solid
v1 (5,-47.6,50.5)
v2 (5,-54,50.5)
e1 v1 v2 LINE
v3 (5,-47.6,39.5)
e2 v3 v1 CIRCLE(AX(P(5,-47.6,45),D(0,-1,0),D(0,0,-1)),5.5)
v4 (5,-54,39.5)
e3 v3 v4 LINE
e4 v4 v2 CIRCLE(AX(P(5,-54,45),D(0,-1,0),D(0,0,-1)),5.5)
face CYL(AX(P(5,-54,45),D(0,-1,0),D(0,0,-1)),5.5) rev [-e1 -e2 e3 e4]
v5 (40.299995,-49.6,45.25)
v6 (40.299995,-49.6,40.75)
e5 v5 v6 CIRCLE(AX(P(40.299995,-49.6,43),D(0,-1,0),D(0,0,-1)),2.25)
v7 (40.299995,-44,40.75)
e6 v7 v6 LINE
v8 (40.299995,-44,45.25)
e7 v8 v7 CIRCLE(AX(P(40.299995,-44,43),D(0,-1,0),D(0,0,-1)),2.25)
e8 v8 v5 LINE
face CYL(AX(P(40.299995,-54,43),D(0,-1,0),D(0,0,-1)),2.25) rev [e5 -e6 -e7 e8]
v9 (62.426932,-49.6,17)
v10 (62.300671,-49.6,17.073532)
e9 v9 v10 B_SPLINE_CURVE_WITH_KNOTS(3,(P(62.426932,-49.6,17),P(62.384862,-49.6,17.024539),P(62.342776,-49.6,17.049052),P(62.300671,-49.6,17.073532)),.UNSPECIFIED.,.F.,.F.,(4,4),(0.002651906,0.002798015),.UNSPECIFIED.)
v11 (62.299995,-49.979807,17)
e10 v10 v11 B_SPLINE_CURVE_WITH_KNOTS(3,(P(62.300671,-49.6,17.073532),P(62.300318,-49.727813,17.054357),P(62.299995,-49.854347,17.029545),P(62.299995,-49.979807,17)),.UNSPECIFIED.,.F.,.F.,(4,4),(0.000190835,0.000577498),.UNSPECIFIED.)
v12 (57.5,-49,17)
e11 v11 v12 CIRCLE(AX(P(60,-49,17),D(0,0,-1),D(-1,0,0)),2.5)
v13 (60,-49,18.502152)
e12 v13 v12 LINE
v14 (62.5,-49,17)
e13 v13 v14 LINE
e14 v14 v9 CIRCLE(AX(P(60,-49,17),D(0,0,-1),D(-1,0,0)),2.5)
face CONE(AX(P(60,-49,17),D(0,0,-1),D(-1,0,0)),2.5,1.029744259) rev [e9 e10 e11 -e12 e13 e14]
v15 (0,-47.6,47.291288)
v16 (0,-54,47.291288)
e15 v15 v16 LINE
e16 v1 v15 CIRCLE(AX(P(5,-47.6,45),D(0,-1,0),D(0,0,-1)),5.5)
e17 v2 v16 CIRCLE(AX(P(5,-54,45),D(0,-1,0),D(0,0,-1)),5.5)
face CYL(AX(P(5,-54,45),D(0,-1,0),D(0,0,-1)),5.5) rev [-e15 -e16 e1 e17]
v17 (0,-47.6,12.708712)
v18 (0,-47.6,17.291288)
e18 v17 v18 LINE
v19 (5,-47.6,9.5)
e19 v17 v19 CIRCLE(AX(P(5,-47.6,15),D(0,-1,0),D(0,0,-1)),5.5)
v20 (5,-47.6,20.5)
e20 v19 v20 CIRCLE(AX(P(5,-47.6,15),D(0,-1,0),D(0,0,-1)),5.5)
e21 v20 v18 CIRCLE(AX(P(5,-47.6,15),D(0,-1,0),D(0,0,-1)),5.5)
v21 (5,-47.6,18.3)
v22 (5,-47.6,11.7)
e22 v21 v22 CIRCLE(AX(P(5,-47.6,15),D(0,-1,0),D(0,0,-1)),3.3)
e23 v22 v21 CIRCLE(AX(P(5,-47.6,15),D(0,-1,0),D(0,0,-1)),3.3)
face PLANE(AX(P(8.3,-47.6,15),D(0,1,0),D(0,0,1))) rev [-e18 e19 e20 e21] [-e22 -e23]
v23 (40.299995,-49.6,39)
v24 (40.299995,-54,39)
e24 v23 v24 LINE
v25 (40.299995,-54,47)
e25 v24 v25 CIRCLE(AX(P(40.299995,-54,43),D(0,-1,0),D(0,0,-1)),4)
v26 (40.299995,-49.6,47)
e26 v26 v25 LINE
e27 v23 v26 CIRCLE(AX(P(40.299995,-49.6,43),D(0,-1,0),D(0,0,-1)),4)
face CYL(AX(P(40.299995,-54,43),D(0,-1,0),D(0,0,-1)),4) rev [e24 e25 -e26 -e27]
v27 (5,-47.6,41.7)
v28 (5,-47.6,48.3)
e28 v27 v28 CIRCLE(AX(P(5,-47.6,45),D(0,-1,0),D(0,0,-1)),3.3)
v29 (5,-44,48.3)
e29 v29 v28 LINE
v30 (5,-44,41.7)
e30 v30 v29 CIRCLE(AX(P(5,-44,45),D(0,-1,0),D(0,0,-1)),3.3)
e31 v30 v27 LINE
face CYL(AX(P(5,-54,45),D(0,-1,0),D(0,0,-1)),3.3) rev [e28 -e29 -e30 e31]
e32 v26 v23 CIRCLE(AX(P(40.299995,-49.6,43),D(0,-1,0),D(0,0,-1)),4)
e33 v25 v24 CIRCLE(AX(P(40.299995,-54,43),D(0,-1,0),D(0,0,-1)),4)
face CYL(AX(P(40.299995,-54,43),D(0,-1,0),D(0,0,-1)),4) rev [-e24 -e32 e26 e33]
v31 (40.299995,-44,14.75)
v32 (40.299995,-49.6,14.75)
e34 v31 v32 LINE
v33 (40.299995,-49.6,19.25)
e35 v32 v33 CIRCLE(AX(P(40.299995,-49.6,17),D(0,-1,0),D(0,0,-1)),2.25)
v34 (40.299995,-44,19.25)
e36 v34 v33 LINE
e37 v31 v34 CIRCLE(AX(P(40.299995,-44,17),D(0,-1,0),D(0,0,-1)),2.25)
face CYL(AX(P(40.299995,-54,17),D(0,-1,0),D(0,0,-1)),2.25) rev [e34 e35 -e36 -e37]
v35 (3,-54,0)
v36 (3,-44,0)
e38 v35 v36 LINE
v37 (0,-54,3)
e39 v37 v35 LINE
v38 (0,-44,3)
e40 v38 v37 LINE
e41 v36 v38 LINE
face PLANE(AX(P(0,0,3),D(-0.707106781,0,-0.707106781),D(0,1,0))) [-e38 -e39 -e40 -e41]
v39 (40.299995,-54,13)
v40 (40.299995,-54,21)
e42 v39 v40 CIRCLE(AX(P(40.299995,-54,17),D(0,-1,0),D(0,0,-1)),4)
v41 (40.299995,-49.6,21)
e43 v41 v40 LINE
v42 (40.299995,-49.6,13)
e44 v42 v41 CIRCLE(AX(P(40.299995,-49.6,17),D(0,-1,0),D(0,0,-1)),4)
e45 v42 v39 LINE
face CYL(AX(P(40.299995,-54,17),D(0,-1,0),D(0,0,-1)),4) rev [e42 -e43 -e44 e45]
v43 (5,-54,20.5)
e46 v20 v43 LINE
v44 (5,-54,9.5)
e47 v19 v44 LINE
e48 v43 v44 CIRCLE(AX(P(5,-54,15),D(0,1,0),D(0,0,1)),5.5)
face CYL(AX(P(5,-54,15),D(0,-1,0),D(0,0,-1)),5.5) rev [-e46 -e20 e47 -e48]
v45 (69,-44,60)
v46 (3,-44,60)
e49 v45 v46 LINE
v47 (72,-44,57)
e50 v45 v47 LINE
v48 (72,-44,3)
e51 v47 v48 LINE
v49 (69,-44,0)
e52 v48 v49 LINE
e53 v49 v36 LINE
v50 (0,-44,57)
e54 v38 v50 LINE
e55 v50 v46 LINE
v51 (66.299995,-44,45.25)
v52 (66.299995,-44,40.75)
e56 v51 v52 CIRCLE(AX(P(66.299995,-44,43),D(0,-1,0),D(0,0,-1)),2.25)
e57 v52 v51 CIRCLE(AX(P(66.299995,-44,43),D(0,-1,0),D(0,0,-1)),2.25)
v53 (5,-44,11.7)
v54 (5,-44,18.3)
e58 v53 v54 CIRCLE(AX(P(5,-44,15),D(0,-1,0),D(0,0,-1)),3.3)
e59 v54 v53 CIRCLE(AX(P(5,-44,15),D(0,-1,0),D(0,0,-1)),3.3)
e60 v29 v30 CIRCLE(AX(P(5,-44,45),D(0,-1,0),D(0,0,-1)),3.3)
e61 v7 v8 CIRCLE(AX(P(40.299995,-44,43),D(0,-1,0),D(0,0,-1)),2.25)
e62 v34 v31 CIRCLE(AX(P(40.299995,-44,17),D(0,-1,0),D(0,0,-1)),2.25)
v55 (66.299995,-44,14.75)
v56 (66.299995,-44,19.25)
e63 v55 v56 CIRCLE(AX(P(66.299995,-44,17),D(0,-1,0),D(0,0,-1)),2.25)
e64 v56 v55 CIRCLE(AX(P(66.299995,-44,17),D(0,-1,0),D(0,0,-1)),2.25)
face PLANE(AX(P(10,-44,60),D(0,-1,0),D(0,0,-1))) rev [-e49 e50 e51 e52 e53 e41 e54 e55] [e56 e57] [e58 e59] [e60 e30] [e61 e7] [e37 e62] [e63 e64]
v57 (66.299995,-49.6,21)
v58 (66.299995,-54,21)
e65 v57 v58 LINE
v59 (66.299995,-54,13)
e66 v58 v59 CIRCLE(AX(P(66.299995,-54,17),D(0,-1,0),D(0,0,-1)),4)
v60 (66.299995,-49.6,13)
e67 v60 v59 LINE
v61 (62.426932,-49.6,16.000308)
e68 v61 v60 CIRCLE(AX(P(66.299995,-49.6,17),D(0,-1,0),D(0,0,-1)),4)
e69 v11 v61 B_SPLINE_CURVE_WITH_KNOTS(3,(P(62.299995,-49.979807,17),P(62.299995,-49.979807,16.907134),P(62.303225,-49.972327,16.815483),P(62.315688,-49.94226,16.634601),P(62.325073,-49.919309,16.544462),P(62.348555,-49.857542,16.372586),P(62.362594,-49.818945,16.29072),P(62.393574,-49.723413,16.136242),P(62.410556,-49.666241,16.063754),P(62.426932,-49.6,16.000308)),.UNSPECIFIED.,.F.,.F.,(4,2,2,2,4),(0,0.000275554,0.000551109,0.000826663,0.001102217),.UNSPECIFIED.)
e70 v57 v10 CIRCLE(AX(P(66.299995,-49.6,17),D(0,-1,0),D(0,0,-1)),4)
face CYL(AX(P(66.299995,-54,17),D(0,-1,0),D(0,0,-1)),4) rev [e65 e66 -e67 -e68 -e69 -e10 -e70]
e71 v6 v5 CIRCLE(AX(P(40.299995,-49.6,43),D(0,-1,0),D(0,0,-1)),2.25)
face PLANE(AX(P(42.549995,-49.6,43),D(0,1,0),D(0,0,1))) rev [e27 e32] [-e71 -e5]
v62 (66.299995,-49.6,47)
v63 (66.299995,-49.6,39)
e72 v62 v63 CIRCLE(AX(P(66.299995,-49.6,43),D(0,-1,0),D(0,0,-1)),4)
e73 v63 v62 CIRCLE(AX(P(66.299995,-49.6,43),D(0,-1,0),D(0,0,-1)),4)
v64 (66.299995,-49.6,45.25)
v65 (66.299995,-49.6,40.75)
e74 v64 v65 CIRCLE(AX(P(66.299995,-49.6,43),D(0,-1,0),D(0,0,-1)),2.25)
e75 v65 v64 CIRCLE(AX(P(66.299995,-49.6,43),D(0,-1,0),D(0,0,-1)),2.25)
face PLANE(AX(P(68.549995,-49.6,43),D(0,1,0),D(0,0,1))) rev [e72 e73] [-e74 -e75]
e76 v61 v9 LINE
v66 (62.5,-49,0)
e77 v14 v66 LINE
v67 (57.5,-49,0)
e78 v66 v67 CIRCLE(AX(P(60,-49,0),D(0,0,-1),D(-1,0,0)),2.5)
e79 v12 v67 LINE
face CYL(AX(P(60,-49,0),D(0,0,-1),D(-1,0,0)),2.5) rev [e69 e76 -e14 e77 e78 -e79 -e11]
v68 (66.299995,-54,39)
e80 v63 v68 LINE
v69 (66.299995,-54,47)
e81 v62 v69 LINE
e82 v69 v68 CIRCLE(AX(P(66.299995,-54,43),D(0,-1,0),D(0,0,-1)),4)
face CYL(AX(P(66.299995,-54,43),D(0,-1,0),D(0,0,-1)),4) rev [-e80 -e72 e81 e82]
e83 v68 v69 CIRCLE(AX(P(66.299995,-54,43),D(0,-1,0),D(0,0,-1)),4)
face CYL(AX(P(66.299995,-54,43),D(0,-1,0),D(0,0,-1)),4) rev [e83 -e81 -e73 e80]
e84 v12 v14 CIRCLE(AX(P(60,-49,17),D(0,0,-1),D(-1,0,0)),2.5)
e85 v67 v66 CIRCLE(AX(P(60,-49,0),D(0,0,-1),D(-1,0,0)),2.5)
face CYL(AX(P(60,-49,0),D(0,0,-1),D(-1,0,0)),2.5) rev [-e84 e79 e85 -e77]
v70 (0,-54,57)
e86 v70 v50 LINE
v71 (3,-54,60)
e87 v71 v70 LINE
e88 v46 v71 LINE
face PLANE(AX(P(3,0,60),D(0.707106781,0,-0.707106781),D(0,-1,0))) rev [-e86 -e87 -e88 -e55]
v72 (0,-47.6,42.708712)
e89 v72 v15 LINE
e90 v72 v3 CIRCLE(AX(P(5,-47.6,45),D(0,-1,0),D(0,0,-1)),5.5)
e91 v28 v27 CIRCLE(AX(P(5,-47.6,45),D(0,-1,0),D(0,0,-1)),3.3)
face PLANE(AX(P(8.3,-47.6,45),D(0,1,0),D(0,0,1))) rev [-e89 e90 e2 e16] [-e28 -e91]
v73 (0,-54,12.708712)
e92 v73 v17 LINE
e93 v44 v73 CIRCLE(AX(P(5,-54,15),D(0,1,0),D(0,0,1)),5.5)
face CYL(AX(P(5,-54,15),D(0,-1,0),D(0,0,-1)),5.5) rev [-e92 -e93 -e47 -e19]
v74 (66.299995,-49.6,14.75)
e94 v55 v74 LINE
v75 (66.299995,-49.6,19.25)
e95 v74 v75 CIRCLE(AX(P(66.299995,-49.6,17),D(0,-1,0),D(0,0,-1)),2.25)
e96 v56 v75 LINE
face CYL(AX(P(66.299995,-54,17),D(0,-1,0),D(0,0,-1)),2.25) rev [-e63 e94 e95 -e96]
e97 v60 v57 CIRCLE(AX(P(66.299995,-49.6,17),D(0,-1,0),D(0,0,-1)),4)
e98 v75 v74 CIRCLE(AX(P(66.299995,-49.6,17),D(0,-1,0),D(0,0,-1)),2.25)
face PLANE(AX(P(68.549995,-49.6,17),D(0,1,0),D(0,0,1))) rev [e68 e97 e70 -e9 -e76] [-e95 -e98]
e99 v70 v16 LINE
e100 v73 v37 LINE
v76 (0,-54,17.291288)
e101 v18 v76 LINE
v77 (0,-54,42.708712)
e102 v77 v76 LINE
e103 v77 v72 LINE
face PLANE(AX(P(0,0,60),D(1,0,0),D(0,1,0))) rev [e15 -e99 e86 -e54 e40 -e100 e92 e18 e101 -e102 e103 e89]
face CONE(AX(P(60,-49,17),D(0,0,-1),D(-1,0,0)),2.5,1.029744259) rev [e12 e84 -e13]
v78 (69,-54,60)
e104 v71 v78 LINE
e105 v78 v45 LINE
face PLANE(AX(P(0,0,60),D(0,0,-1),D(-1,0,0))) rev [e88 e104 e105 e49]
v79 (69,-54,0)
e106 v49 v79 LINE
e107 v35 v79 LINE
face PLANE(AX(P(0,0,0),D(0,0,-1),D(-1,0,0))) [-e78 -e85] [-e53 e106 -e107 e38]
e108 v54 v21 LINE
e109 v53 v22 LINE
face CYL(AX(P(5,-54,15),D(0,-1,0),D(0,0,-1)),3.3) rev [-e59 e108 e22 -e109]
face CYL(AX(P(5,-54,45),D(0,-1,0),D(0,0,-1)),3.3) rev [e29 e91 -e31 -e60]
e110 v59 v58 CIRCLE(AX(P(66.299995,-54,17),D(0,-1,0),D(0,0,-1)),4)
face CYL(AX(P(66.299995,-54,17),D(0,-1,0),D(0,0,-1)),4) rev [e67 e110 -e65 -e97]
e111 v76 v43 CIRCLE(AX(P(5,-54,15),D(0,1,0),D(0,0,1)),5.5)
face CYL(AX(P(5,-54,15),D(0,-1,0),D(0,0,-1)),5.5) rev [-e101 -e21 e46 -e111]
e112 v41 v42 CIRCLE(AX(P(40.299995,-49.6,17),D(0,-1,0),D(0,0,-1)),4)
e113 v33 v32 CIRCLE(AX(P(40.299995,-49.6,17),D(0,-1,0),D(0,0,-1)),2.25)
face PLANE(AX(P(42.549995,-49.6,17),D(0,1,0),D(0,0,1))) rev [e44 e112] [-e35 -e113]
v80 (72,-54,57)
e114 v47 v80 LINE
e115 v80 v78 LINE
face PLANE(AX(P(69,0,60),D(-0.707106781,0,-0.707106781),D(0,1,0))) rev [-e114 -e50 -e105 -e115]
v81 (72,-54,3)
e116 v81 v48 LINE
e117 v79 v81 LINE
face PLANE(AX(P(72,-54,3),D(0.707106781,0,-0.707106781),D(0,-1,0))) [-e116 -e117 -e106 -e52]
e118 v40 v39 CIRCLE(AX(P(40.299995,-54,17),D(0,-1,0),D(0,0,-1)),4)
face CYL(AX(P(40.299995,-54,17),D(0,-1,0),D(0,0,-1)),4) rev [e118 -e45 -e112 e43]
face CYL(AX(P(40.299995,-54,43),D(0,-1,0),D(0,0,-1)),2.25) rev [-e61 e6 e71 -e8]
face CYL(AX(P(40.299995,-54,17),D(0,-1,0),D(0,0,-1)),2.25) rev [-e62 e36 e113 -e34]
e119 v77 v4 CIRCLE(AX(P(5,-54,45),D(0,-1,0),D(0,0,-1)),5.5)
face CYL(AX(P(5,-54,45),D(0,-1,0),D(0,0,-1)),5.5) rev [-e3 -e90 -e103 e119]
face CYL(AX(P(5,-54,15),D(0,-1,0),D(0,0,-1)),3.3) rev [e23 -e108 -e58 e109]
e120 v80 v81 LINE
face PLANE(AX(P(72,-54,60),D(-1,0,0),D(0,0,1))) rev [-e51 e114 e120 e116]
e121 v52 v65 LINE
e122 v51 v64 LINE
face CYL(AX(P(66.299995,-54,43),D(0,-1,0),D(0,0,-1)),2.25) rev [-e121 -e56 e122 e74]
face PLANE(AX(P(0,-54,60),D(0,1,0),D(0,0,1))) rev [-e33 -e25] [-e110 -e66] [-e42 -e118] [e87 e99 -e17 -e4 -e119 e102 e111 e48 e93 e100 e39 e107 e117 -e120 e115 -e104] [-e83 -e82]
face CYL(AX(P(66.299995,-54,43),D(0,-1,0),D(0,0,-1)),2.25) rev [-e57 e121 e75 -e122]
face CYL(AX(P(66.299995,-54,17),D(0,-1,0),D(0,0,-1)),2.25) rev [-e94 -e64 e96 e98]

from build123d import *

# Parameters (mm, degrees)
EXTRUDE_1_DEPTH                = 60
HOLE_WIZARD_M6_2_D             = 5
HOLE_WIZARD_M6_2_DEPTH         = 17
HOLE_WIZARD_M6_2_TIP           = 1.502151548
HOLE_WIZARD_M4_1_D             = 4.5
HOLE_WIZARD_M4_1_DEPTH         = 11.5
HOLE_WIZARD_M4_1_CBORE_D       = 8
HOLE_WIZARD_M4_1_CBORE_DEPTH   = 4.4
HOLE_WIZARD_M4_1_TIP           = 1.351936393
HOLE_WIZARD_M6_1_D             = 5
HOLE_WIZARD_M6_1_DEPTH         = 17
HOLE_WIZARD_M6_1_TIP           = 1.502151548
CHAMFER_1_SIZE                 = 3
SKETCH_9_W                     = 10
SKETCH_9_H                     = 44
CUT_EXTRUDE_1_DEPTH            = 109.166538369
CHAMFER_2_SIZE                 = 3
HOLE_WIZARD_M6_1_2_D           = 6.6
HOLE_WIZARD_M6_1_2_DEPTH       = 17
HOLE_WIZARD_M6_1_2_CBORE_D     = 11
HOLE_WIZARD_M6_1_2_CBORE_DEPTH = 6.4
HOLE_WIZARD_M6_1_2_TIP         = 1.982840043


with BuildPart() as part:
    # 草图2 → 凸台-拉伸1 (new body)
    with BuildSketch(Plane.XY):
        Polygon((0, 0), (0, -54), (72, -54), (72, -44), (10, -44), (10, 0), align=None)
    extrude(amount=EXTRUDE_1_DEPTH)

    # M6 螺纹孔2
    with Locations(Plane(origin=(0, 0, 0), x_dir=(-1, 0, 0), z_dir=(0, 0, -1))):
        with Locations((-60, -49)):
            Hole(HOLE_WIZARD_M6_2_D / 2, depth=HOLE_WIZARD_M6_2_DEPTH)
            with Locations((0, 0, -(HOLE_WIZARD_M6_2_DEPTH + HOLE_WIZARD_M6_2_TIP / 2))):  # 118° drill point
                Cone(0, HOLE_WIZARD_M6_2_D / 2, HOLE_WIZARD_M6_2_TIP, mode=Mode.SUBTRACT)

    # M4 六角凹头螺钉的柱形沉头孔1
    with Locations(Plane(origin=(0, -54, 0), x_dir=(-1, 0, 0), z_dir=(0, -1, 0))):
        with Locations((-40.299995099, -17), (-66.299995099, -17), (-66.299995099, -43), (-40.299995099, -43)):
            CounterBoreHole(HOLE_WIZARD_M4_1_D / 2, HOLE_WIZARD_M4_1_CBORE_D / 2, HOLE_WIZARD_M4_1_CBORE_DEPTH, depth=HOLE_WIZARD_M4_1_DEPTH)
            with Locations((0, 0, -(HOLE_WIZARD_M4_1_DEPTH + HOLE_WIZARD_M4_1_TIP / 2))):  # 118° drill point
                Cone(0, HOLE_WIZARD_M4_1_D / 2, HOLE_WIZARD_M4_1_TIP, mode=Mode.SUBTRACT)

    # Hole Wizard M6 _1
    with Locations(Plane(origin=(0, 0, 0), x_dir=(1, 0, 0), z_dir=(0, 1, 0))):
        with Locations((5, -15), (5, -45)):
            Hole(HOLE_WIZARD_M6_1_D / 2, depth=HOLE_WIZARD_M6_1_DEPTH)
            with Locations((0, 0, -(HOLE_WIZARD_M6_1_DEPTH + HOLE_WIZARD_M6_1_TIP / 2))):  # 118° drill point
                Cone(0, HOLE_WIZARD_M6_1_D / 2, HOLE_WIZARD_M6_1_TIP, mode=Mode.SUBTRACT)

    # 倒角1
    chamfer_1_edges = [part.edges().sort_by_distance(p)[0] for p in [
        (72, -49, 60),
        (5, 0, 60),
        (72, -49, 0),
        (5, 0, 0),
    ]]
    chamfer(chamfer_1_edges, length=CHAMFER_1_SIZE)

    # 草图9 → 切除-拉伸1 (cut, through all)
    with BuildSketch(Plane.XY.offset(60)):
        with Locations((5, -22)):
            Rectangle(SKETCH_9_W, SKETCH_9_H)
    extrude(amount=-CUT_EXTRUDE_1_DEPTH, mode=Mode.SUBTRACT)

    # 倒角2
    chamfer_2_edges = [part.edges().sort_by_distance(p)[0] for p in [
        (0, -49, 0),
        (0, -49, 60),
    ]]
    chamfer(chamfer_2_edges, length=CHAMFER_2_SIZE)

    # Hole Wizard M6 _1 2
    with Locations(Plane(origin=(0, -54, 0), x_dir=(-1, 0, 0), z_dir=(0, -1, 0))):
        with Locations((-5, -15), (-5, -45)):
            CounterBoreHole(HOLE_WIZARD_M6_1_2_D / 2, HOLE_WIZARD_M6_1_2_CBORE_D / 2, HOLE_WIZARD_M6_1_2_CBORE_DEPTH, depth=HOLE_WIZARD_M6_1_2_DEPTH)
            with Locations((0, 0, -(HOLE_WIZARD_M6_1_2_DEPTH + HOLE_WIZARD_M6_1_2_TIP / 2))):  # 118° drill point
                Cone(0, HOLE_WIZARD_M6_1_2_D / 2, HOLE_WIZARD_M6_1_2_TIP, mode=Mode.SUBTRACT)


solid = part.part
